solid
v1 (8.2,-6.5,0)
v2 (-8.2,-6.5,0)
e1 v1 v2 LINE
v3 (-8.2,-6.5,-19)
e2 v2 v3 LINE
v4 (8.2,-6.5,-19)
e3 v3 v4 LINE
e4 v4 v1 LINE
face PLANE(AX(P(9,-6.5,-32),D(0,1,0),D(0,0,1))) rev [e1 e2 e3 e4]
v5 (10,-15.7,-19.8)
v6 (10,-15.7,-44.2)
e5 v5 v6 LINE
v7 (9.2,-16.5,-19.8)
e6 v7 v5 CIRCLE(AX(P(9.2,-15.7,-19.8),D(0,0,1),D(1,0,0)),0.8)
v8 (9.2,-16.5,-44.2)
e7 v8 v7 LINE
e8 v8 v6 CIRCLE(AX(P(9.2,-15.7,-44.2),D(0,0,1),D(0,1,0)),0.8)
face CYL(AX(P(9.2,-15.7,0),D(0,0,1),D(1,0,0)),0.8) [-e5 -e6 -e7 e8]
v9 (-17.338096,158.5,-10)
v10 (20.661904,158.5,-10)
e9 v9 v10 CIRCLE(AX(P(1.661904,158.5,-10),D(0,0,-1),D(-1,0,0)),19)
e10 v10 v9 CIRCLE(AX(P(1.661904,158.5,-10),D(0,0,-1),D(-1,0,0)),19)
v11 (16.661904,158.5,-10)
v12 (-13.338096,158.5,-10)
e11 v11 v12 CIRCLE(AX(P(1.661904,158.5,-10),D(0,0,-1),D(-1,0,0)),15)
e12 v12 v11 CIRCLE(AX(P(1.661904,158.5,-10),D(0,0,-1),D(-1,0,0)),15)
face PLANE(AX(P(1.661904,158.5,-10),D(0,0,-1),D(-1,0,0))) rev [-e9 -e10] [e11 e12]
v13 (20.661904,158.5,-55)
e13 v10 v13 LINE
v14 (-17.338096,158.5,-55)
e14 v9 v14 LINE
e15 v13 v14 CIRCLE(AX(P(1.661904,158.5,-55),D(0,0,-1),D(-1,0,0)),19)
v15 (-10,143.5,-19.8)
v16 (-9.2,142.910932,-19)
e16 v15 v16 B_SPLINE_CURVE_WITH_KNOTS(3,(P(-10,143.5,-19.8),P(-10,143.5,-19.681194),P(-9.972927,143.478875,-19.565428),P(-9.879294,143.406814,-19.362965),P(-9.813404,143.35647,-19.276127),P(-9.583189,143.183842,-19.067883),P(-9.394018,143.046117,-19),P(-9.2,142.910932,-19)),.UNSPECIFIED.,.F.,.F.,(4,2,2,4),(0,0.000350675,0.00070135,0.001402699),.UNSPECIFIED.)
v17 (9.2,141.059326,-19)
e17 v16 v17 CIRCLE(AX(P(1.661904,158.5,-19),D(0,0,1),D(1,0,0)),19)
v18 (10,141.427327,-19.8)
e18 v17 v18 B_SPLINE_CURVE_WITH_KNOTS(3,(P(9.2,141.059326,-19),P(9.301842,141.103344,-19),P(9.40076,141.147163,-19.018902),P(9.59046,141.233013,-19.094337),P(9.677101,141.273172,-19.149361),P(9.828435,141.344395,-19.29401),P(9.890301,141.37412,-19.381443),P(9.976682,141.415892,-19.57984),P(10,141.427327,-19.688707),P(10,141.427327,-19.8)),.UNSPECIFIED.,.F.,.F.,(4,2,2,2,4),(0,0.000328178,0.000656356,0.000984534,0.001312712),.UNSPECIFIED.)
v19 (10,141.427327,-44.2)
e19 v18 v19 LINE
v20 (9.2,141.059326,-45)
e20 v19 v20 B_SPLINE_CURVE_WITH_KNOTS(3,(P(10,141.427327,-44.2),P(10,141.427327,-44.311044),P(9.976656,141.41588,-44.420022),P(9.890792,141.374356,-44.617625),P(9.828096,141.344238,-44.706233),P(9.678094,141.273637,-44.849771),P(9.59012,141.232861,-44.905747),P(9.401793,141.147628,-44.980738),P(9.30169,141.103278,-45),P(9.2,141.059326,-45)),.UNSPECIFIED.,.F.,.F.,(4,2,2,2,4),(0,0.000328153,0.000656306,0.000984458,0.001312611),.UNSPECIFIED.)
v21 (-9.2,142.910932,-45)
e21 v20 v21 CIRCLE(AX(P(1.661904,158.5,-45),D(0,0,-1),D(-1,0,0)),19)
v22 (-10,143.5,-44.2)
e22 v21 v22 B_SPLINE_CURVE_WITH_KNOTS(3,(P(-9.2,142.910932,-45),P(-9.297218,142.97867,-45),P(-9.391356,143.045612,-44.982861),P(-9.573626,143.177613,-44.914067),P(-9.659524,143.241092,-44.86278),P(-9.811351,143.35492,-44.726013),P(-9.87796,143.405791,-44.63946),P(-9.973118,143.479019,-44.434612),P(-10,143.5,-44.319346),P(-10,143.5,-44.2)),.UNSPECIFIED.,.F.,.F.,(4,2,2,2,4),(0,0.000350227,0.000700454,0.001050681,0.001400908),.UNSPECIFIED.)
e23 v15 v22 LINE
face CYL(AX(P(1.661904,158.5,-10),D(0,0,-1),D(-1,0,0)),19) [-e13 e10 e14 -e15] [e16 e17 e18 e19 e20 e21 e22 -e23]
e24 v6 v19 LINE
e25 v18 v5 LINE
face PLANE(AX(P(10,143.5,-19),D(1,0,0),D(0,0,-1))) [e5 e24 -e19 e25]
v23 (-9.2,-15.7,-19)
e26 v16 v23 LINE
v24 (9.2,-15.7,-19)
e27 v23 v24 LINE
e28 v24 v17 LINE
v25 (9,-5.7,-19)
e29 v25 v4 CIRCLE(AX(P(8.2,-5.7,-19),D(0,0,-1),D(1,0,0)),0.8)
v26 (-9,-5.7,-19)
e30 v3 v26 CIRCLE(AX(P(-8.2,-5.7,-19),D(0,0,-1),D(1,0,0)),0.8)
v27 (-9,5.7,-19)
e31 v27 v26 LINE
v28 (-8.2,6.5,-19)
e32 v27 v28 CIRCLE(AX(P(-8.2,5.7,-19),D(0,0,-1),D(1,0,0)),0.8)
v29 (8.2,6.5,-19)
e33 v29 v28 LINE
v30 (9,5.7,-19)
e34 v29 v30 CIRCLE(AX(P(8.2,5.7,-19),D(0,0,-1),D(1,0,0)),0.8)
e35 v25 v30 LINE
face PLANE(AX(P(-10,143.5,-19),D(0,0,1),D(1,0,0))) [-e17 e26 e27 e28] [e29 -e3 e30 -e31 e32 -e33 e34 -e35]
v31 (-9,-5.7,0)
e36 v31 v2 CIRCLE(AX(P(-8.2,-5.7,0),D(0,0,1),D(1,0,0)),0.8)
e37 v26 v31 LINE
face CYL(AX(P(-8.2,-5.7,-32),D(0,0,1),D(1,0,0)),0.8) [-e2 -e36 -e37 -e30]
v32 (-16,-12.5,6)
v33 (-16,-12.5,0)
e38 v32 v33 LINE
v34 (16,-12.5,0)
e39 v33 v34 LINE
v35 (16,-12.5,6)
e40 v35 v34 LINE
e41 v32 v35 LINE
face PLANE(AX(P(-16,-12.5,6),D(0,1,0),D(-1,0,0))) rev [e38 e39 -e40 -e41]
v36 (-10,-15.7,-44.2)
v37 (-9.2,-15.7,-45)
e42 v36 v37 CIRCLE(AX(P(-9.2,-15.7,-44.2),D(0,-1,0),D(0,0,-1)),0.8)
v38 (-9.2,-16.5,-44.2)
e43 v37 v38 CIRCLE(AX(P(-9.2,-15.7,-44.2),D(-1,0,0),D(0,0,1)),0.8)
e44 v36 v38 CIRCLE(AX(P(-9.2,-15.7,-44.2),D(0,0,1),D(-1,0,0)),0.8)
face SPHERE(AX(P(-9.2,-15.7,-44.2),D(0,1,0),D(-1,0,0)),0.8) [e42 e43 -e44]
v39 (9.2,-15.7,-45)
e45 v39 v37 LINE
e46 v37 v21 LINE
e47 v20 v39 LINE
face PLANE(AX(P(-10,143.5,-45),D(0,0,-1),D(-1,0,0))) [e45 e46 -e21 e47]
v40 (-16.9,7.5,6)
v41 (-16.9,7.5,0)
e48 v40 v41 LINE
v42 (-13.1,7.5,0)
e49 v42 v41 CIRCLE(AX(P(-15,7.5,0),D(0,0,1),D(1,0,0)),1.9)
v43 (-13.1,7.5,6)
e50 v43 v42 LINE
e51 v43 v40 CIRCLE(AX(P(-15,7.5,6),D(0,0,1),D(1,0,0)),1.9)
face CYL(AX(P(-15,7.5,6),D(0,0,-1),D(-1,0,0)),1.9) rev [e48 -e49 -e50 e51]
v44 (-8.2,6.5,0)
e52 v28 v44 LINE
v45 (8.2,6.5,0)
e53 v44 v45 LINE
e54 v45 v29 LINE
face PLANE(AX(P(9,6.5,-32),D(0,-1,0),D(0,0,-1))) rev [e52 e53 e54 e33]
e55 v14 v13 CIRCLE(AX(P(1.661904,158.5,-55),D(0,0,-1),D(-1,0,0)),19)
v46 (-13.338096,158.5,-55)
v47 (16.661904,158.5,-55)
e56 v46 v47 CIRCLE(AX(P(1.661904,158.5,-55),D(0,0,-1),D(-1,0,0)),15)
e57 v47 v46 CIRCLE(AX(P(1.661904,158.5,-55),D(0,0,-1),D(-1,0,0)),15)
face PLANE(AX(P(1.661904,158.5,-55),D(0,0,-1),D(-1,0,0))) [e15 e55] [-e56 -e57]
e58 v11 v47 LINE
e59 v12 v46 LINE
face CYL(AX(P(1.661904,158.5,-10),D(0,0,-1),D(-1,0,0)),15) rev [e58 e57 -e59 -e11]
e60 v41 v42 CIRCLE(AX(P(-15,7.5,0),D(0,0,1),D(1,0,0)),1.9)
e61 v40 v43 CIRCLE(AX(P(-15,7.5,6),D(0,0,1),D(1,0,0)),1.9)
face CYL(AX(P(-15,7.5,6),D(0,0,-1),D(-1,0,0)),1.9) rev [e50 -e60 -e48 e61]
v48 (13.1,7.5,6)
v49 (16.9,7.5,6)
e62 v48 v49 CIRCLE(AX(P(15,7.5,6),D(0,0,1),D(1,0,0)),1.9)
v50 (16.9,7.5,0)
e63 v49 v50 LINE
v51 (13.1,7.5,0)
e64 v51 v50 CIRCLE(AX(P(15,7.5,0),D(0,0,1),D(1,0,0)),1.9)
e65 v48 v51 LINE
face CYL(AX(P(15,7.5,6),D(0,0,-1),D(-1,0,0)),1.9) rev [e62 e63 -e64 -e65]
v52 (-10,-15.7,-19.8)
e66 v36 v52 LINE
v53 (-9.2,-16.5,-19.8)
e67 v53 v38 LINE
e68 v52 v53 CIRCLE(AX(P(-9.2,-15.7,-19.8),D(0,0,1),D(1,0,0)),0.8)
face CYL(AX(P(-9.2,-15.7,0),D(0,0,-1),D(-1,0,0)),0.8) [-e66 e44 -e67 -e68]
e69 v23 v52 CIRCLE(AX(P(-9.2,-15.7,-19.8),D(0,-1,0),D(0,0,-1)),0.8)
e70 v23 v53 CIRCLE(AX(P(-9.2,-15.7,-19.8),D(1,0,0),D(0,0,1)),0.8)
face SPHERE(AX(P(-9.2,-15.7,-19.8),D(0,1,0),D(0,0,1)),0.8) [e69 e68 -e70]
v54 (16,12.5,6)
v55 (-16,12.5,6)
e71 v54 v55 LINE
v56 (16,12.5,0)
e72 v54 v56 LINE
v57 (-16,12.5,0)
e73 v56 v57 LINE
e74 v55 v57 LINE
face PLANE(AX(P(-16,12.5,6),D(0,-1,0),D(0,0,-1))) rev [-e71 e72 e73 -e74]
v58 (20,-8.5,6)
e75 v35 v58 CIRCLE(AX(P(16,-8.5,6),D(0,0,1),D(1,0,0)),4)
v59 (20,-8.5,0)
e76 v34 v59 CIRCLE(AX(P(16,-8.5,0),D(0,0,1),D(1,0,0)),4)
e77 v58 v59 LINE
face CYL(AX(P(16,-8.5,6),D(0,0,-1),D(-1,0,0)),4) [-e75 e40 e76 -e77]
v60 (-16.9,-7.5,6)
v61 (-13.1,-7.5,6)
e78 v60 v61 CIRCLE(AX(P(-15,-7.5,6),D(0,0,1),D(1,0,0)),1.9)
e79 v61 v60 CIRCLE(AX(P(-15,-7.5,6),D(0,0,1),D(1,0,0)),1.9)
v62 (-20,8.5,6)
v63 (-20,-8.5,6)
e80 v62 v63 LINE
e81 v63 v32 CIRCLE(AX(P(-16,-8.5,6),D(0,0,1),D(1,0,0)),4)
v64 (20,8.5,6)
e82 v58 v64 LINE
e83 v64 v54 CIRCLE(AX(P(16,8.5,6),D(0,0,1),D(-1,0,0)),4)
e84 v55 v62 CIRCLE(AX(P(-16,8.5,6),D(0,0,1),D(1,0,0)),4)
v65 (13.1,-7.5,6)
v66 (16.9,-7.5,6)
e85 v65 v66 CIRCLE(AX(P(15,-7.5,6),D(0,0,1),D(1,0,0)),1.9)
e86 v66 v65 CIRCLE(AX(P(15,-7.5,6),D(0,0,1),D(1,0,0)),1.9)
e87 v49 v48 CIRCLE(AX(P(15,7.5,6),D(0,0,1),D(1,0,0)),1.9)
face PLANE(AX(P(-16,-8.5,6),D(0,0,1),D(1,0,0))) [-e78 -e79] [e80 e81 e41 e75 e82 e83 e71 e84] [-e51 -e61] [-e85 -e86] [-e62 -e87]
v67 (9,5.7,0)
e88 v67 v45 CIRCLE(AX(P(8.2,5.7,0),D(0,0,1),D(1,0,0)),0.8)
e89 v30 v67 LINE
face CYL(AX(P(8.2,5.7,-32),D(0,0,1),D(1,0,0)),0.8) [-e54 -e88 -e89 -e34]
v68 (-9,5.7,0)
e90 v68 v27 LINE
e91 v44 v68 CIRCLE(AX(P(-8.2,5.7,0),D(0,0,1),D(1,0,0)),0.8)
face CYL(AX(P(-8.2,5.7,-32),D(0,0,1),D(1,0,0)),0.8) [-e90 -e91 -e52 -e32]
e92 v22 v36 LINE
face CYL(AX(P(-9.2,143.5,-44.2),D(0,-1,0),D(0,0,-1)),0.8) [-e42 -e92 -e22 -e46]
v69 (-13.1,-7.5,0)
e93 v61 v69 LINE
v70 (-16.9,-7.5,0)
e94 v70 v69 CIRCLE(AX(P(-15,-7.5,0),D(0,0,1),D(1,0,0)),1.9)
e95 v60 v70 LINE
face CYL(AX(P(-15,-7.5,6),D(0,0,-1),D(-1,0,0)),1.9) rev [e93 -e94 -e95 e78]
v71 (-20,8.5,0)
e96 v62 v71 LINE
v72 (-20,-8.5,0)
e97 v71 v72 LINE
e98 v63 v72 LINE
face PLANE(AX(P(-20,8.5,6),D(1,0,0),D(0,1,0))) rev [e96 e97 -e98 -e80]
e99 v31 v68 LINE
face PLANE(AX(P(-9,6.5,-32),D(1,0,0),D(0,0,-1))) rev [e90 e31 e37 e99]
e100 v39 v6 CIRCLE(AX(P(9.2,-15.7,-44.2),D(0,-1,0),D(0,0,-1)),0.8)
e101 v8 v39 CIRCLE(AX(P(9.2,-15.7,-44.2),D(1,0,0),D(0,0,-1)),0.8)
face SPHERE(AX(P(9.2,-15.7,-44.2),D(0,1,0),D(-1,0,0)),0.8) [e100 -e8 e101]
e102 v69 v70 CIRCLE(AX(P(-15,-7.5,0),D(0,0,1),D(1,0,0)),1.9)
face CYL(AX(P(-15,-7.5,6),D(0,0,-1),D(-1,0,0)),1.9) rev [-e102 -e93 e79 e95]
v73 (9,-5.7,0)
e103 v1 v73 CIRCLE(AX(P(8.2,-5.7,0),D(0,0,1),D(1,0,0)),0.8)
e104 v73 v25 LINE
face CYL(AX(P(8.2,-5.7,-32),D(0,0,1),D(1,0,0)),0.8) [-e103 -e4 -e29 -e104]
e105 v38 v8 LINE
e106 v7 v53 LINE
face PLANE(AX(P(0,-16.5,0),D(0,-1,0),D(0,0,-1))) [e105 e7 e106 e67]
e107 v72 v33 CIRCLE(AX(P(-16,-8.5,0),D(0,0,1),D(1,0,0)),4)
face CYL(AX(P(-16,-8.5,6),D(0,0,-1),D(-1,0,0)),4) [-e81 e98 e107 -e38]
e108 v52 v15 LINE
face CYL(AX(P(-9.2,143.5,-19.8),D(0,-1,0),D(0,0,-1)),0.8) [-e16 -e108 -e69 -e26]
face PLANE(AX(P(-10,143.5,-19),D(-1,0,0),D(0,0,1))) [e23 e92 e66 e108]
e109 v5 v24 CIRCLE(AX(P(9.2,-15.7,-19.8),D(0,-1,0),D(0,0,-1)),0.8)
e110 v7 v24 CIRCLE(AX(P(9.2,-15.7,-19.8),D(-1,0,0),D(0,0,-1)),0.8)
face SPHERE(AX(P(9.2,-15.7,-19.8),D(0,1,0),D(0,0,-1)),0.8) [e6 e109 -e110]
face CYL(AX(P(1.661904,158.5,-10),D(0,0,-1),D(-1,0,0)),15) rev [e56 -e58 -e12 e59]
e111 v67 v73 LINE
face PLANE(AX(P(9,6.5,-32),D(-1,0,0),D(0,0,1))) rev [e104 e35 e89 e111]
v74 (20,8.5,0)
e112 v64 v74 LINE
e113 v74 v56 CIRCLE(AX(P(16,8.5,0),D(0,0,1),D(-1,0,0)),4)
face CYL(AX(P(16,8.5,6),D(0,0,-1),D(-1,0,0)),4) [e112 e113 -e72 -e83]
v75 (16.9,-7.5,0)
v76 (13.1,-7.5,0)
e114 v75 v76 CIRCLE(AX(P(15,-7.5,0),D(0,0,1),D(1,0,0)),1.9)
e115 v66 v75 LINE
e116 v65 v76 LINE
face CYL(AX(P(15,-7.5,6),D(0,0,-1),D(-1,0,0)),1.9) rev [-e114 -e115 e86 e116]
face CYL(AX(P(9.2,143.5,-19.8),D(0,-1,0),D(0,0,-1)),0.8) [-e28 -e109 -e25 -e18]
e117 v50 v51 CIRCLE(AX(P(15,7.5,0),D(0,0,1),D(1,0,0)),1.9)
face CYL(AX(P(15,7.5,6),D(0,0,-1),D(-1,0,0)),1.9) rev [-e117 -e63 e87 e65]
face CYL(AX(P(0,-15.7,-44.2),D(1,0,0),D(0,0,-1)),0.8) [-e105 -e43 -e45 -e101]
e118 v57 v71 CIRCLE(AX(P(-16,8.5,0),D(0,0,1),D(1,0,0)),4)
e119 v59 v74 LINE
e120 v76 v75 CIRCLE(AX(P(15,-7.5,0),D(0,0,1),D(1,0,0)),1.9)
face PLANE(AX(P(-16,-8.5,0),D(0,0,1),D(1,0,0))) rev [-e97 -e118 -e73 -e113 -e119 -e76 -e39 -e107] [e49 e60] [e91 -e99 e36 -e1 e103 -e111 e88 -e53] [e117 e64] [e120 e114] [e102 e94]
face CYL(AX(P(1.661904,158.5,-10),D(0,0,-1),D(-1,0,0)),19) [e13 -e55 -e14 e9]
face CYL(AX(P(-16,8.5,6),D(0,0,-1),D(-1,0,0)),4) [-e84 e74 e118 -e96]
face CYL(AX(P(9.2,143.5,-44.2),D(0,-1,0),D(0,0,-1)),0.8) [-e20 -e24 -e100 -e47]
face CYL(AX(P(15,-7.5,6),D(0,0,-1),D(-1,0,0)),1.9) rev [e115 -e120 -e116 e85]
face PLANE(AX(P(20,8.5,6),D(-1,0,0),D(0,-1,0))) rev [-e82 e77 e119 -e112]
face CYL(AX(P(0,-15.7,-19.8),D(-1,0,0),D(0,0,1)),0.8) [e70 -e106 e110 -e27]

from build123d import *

# Parameters (mm, degrees)
SKETCH1_R                = 1.9
BOSS_EXTRUDE1_DEPTH      = 6
SKETCH2_W                = 18
SKETCH2_H                = 13
BOSS_EXTRUDE2_DEPTH      = 32
BOSS_EXTRUDE3_DEPTH      = 10
BOSS_EXTRUDE3_DEPTH_BACK = 150
SKETCH4_W                = 20
SKETCH4_H                = 26
BOSS_EXTRUDE4_DEPTH      = 10
BOSS_EXTRUDE4_DEPTH_BACK = 35
SKETCH5_R                = 19
SKETCH5_R_2              = 15
FILLET1_R                = 0.8


with BuildPart() as part:
    # Sketch1 → Boss-Extrude1 (new body)
    with BuildSketch(Plane.XY):
        with BuildLine():
            Line((-16, 12.5), (16, 12.5))
            ThreePointArc((16, 12.5), (18.828427125, 11.328427125), (20, 8.5))
            Line((20, 8.5), (20, -8.5))
            ThreePointArc((20, -8.5), (18.828427125, -11.328427125), (16, -12.5))
            Line((16, -12.5), (-16, -12.5))
            ThreePointArc((-16, -12.5), (-18.828427125, -11.328427125), (-20, -8.5))
            Line((-20, -8.5), (-20, 8.5))
            ThreePointArc((-20, 8.5), (-18.828427125, 11.328427125), (-16, 12.5))
        make_face()
        with Locations((-15, 7.5)):
            Circle(SKETCH1_R, mode=Mode.SUBTRACT)
        with Locations((15, 7.5)):
            Circle(SKETCH1_R, mode=Mode.SUBTRACT)
        with Locations((15, -7.5)):
            Circle(SKETCH1_R, mode=Mode.SUBTRACT)
        with Locations((-15, -7.5)):
            Circle(SKETCH1_R, mode=Mode.SUBTRACT)
    extrude(amount=BOSS_EXTRUDE1_DEPTH)

    # Sketch2 → Boss-Extrude2 (add)
    with BuildSketch(Plane(origin=(0, 0, 0), x_dir=(-1, 0, 0), z_dir=(0, 0, -1))):
        Rectangle(SKETCH2_W, SKETCH2_H)
    extrude(amount=BOSS_EXTRUDE2_DEPTH)

    # Sketch4 → Boss-Extrude3 (add, two sides: drawn at the far end of the back side and taken through both)
    with BuildSketch(Plane(origin=(0, -6.5, 0), x_dir=(-1, 0, 0), z_dir=(0, -1, 0)).offset(-BOSS_EXTRUDE3_DEPTH_BACK)):
        with Locations((0, 32)):
            Rectangle(SKETCH4_W, SKETCH4_H)
    extrude(amount=BOSS_EXTRUDE3_DEPTH + BOSS_EXTRUDE3_DEPTH_BACK)

    # Sketch5 → Boss-Extrude4 (add, two sides: drawn at the far end of the back side and taken through both)
    with BuildSketch(Plane(origin=(0, 0, -45), x_dir=(-1, 0, 0), z_dir=(0, 0, -1)).offset(-BOSS_EXTRUDE4_DEPTH_BACK)):
        with Locations((-1.66190379, 158.5)):
            Circle(SKETCH5_R)
        with Locations((-1.66190379, 158.5)):
            Circle(SKETCH5_R_2, mode=Mode.SUBTRACT)
    extrude(amount=BOSS_EXTRUDE4_DEPTH + BOSS_EXTRUDE4_DEPTH_BACK)

    # Fillet1
    fillet1_edges = [part.edges().sort_by_distance(p)[0] for p in [
        (-9, -6.5, -9.5),
        (9, -6.5, -9.5),
        (9, 6.5, -9.5),
        (-9, 6.5, -9.5),
        (-10, 63.5, -19),
        (-10, 63.5, -45),
        (10, -16.5, -32),
        (0, -16.5, -19),
        (-10, -16.5, -32),
        (0, -16.5, -45),
        (10, 62.463663672, -45),
        (10, 62.463663672, -19),
    ]]
    fillet(fillet1_edges, radius=FILLET1_R)


solid = part.part
